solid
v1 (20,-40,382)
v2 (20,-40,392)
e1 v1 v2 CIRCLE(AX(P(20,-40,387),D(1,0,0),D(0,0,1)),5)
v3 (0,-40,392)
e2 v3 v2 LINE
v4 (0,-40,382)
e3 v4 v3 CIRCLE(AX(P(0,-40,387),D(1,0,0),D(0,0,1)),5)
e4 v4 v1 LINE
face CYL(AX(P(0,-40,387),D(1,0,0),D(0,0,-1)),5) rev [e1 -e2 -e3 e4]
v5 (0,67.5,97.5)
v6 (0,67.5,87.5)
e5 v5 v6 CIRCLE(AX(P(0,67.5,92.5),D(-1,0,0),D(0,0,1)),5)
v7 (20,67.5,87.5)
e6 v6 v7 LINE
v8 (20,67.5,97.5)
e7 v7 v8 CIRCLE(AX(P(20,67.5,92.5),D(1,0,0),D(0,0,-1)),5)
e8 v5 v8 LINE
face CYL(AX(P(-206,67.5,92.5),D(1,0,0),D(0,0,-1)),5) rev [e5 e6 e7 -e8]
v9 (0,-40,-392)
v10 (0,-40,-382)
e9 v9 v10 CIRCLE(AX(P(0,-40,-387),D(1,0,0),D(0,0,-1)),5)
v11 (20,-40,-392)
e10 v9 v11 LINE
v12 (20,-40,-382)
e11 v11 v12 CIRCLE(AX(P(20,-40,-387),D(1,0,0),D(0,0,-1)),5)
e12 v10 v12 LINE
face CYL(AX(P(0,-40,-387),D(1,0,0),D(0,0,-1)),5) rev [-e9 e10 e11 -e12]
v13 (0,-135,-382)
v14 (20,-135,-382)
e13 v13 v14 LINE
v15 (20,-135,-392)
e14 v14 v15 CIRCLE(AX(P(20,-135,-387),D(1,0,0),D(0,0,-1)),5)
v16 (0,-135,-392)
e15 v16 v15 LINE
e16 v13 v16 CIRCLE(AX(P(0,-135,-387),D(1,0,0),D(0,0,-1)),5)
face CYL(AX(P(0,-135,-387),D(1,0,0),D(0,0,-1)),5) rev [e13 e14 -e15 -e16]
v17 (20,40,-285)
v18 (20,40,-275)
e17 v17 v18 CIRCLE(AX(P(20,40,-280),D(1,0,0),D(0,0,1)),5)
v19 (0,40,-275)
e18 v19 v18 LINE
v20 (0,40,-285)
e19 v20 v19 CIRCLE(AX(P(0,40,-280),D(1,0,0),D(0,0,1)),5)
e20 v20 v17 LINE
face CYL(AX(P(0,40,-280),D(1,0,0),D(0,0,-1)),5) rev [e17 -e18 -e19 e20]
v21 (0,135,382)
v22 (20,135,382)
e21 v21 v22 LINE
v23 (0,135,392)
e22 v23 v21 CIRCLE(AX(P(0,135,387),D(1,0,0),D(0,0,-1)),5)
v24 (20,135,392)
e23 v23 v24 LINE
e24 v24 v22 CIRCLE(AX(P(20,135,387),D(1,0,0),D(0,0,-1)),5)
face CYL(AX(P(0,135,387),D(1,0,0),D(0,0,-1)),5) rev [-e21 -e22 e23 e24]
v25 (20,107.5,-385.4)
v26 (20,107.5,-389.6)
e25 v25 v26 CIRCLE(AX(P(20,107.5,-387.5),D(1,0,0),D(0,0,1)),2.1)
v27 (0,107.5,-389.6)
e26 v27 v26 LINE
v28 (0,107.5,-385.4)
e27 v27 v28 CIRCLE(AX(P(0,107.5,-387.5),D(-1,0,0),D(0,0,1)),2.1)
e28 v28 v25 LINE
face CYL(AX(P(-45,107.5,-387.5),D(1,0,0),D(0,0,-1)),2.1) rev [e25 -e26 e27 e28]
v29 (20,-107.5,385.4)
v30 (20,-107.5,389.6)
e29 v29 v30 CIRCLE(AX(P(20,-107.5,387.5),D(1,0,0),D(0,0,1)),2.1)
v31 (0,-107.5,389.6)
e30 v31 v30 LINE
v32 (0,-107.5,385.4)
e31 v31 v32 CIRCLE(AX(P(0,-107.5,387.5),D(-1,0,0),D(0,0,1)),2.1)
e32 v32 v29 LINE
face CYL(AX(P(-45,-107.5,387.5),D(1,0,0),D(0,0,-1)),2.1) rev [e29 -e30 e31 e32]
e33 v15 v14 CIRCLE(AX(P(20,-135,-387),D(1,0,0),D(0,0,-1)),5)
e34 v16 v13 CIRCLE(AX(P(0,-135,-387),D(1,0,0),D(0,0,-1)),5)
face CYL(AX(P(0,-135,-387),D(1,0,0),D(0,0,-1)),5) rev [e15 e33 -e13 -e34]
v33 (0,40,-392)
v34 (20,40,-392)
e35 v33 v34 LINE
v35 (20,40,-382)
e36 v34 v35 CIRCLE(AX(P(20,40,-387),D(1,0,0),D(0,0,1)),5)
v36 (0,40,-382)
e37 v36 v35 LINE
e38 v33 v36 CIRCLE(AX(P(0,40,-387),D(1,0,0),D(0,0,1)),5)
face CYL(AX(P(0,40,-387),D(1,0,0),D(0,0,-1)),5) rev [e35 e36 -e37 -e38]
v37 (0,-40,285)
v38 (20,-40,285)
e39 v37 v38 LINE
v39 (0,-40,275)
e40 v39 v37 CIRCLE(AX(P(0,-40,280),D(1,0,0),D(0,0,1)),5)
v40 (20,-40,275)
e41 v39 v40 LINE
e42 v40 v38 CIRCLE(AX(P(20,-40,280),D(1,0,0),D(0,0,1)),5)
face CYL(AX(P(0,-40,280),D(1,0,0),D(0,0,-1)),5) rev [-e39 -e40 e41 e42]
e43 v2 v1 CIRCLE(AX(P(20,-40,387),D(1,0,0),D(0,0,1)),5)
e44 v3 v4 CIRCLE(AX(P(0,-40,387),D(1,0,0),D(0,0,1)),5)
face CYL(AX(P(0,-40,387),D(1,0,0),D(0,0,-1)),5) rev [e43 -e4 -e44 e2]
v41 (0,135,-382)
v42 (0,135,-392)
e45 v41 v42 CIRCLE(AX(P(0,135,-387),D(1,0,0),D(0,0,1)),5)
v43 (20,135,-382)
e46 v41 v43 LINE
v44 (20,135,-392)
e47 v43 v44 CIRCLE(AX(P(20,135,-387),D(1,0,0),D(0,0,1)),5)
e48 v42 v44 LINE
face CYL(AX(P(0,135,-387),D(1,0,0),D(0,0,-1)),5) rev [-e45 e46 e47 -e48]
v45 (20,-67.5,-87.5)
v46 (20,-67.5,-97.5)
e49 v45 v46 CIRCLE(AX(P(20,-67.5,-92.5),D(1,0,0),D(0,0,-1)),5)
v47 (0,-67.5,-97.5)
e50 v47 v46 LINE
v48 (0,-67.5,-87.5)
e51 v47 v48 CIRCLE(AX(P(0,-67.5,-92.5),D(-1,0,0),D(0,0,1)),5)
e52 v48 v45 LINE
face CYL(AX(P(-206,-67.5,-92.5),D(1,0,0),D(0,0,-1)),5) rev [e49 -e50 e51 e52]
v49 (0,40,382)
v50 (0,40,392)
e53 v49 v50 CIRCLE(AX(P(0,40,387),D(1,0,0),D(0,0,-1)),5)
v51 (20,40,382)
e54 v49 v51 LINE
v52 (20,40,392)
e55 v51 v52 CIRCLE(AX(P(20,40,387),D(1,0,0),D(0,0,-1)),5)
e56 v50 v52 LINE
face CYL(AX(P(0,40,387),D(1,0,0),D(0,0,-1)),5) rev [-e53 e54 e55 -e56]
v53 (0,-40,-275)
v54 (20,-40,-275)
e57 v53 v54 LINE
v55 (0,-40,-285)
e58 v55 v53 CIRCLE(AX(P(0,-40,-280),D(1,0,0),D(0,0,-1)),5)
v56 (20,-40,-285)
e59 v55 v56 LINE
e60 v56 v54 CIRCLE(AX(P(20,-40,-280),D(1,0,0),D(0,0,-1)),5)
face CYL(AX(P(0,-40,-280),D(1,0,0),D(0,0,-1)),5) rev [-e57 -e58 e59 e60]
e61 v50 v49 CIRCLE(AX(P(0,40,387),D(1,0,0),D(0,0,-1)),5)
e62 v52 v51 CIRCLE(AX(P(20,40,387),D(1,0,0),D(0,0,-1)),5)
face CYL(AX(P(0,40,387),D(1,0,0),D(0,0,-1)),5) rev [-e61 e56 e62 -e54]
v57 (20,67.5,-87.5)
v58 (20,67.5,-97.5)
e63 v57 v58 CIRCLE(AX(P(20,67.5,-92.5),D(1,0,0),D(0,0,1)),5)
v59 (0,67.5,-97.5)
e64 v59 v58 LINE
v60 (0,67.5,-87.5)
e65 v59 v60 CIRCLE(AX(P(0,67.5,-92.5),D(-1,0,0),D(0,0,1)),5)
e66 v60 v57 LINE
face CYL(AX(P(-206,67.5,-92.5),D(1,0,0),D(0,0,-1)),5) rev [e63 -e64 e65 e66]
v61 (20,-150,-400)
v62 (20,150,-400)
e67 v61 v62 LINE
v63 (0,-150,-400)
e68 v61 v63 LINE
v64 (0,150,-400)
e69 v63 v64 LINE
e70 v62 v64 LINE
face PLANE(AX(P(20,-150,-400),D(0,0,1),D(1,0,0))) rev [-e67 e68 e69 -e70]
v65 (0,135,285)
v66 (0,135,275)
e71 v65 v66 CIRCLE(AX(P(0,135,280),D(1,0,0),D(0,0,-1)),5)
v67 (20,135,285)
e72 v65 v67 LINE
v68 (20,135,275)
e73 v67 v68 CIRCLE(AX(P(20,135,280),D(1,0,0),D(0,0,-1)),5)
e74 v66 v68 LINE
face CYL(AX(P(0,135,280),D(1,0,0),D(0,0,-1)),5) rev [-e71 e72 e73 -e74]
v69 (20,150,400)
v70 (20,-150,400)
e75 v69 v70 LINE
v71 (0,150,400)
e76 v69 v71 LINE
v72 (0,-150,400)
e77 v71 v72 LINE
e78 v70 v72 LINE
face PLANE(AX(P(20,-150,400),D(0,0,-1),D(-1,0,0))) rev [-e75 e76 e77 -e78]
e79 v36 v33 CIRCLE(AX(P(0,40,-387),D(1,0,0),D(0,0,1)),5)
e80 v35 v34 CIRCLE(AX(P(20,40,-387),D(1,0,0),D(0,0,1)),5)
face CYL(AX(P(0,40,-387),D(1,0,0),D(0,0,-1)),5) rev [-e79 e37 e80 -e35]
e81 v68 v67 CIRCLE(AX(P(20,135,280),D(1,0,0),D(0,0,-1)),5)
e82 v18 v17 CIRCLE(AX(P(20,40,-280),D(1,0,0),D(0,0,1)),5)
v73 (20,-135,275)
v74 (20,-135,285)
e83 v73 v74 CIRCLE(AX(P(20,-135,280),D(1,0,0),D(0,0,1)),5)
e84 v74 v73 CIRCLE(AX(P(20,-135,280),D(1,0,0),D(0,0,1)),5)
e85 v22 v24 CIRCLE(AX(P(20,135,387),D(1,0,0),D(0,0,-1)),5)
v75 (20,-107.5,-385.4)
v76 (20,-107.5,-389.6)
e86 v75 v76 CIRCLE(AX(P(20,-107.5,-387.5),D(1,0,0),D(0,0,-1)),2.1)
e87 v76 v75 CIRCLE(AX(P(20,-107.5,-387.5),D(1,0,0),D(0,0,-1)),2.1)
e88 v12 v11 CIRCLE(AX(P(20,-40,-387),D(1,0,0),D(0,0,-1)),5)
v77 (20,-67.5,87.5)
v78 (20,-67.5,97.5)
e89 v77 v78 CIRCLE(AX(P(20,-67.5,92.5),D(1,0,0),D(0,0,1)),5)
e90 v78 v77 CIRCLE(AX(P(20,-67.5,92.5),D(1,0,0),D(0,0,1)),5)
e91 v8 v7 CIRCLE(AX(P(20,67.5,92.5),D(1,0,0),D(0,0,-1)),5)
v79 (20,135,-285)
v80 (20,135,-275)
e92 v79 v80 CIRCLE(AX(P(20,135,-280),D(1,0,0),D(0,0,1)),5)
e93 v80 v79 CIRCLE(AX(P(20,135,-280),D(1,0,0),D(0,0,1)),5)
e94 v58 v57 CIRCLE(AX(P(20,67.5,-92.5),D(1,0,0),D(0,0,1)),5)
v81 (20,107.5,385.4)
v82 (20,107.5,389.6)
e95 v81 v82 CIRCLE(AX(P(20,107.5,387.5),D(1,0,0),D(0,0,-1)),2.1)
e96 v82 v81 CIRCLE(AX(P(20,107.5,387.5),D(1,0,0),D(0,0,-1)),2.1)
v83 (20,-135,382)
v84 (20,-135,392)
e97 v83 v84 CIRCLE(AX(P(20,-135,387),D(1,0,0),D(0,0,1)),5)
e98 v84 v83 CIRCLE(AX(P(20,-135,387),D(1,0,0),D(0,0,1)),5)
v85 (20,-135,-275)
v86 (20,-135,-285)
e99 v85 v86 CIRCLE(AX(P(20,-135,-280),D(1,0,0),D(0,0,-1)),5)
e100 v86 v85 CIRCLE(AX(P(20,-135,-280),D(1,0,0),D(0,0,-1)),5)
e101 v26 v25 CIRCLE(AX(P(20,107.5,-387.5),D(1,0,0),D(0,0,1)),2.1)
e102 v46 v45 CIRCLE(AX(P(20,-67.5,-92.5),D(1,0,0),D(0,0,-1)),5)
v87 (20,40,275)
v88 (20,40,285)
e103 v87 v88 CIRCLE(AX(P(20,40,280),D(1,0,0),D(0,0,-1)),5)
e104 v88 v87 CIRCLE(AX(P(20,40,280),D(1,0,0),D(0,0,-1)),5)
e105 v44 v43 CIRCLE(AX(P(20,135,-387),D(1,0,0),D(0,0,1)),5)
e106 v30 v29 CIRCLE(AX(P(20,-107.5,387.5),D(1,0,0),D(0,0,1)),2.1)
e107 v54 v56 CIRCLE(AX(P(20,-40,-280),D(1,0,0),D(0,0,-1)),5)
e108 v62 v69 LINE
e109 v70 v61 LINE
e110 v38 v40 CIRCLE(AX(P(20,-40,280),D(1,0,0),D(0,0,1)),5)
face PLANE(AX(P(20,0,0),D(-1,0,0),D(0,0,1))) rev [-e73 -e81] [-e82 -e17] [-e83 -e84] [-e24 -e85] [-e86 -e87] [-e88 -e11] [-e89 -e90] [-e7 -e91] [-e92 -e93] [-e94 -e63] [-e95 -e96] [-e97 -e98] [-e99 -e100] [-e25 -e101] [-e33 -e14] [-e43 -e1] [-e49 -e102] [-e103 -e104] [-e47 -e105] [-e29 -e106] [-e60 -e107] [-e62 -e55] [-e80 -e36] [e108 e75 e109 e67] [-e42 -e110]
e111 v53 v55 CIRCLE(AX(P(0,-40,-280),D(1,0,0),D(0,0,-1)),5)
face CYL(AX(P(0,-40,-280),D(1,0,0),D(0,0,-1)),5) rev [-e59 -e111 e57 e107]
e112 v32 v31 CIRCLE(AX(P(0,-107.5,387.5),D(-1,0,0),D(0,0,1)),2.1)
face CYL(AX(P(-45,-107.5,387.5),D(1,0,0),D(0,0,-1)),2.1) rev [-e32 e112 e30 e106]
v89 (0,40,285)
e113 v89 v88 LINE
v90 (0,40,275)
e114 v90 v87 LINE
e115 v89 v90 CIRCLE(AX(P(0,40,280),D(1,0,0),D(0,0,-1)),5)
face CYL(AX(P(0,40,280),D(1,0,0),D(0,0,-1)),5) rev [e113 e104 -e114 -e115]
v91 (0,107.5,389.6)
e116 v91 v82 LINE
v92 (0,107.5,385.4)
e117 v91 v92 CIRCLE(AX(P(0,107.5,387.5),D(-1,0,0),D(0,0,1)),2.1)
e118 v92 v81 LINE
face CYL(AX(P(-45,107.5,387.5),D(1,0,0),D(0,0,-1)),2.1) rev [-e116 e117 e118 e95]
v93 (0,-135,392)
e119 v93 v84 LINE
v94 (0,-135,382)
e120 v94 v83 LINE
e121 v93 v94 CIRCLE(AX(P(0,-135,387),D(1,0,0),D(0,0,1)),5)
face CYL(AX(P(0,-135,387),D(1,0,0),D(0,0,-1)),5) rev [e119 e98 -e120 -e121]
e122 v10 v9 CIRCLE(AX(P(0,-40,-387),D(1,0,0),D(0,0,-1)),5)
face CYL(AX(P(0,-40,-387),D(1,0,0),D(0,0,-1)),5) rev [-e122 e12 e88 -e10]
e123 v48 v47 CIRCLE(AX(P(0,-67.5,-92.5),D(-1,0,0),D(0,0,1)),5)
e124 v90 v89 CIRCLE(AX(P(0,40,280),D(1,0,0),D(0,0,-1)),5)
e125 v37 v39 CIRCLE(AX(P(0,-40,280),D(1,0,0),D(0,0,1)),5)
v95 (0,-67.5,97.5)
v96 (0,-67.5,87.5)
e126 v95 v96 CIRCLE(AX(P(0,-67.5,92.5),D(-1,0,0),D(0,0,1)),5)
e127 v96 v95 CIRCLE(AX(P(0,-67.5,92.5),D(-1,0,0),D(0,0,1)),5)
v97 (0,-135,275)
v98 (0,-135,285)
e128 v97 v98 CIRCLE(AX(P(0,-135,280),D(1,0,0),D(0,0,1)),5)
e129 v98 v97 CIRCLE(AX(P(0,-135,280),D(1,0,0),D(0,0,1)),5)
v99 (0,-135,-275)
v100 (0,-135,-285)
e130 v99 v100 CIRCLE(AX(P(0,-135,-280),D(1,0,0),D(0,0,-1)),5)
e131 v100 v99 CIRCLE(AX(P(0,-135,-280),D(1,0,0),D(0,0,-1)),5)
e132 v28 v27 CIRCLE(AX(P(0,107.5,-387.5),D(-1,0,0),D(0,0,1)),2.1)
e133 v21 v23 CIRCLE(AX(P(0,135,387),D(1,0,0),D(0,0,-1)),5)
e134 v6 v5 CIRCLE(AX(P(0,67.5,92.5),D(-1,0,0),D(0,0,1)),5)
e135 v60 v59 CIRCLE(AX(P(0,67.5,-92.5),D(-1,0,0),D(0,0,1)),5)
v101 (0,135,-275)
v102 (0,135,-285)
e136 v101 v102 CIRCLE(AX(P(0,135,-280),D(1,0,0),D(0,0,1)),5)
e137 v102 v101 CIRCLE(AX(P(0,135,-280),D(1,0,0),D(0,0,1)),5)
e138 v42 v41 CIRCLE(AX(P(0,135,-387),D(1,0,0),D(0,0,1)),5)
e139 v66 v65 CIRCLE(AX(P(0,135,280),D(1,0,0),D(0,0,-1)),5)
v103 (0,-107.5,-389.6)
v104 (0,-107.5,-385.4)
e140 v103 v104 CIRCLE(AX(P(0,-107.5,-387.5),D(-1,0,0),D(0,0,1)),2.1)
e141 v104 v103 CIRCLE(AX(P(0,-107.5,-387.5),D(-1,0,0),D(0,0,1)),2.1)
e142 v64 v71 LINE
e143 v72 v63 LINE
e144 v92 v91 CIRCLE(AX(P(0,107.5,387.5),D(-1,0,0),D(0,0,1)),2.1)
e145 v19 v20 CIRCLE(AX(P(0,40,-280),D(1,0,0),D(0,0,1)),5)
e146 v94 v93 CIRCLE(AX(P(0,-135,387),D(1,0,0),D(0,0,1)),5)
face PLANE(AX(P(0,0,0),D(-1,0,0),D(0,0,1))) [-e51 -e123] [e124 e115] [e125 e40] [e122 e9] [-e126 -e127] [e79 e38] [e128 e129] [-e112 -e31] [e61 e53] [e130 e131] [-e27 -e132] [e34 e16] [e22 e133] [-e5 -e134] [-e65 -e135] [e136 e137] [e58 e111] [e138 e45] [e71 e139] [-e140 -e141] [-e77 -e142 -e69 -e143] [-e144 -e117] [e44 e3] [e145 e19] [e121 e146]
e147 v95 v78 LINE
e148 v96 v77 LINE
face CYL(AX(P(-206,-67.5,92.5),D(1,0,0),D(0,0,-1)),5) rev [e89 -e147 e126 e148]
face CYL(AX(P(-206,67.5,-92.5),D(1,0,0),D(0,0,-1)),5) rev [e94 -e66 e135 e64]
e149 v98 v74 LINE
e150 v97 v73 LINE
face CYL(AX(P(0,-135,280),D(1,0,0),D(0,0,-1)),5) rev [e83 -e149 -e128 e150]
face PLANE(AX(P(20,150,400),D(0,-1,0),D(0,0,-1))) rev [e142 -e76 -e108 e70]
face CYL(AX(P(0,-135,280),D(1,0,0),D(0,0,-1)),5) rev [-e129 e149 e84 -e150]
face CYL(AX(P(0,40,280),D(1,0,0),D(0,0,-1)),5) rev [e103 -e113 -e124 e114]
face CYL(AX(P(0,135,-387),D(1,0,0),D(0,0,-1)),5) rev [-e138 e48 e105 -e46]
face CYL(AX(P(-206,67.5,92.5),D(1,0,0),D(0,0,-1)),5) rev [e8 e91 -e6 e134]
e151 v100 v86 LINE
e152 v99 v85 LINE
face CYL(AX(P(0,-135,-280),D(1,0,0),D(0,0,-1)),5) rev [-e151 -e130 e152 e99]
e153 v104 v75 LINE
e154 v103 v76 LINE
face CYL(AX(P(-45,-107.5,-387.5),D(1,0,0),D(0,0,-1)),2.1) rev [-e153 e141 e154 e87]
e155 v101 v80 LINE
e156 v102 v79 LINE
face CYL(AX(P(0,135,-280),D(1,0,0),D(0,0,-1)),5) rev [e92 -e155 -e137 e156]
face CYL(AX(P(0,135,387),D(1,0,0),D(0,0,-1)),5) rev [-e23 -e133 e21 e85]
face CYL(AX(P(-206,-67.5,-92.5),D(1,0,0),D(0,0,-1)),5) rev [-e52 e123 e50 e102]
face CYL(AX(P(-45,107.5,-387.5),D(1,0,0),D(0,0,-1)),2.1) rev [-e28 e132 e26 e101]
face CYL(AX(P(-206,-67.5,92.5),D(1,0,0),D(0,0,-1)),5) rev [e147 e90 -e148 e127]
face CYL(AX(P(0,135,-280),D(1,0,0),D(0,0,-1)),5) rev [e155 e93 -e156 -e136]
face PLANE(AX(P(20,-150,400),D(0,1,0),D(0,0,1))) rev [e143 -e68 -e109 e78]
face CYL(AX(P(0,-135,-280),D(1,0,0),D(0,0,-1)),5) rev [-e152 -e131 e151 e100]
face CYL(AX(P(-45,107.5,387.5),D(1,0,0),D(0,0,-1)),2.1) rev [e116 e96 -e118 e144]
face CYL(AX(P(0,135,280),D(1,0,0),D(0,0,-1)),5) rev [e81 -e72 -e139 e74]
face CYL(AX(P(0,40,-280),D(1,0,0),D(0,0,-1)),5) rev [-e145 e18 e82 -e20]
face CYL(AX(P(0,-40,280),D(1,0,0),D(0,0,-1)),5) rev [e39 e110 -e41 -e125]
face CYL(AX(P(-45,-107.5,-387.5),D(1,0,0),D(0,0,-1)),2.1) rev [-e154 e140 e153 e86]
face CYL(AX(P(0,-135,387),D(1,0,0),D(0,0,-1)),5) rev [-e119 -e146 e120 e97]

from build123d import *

# Parameters (mm, degrees)
SKETCH1_W           = 800
SKETCH1_H           = 300
BOSS_EXTRUDE1_DEPTH = 20
SKETCH2_R           = 5
CUT_EXTRUDE1_DEPTH  = 20
SKETCH3_R           = 2.1
CUT_EXTRUDE2_DEPTH  = 65
SKETCH4_R           = 5
CUT_EXTRUDE3_DEPTH  = 226


with BuildPart() as part:
    # Sketch1 → Boss-Extrude1 (new body)
    with BuildSketch(Plane(origin=(0, 0, 0), x_dir=(0, 0, -1), z_dir=(1, 0, 0))):
        Rectangle(SKETCH1_W, SKETCH1_H)
    extrude(amount=BOSS_EXTRUDE1_DEPTH)

    # Sketch2 → Cut-Extrude1 (cut)
    with BuildSketch(Plane(origin=(20, 0, 0), x_dir=(0, 0, -1), z_dir=(1, 0, 0))):
        with Locations((-387, 135)):
            Circle(SKETCH2_R)
        with Locations((-280, 135)):
            Circle(SKETCH2_R)
        with Locations((-280, 40)):
            Circle(SKETCH2_R)
        with Locations((-387, 40)):
            Circle(SKETCH2_R)
        with Locations(Location((-280, -40, 0), (0, 0, 180))):
            Circle(SKETCH2_R)
        with Locations(Location((-280, -135, 0), (0, 0, 180))):
            Circle(SKETCH2_R)
        with Locations(Location((-387, -135, 0), (0, 0, 180))):
            Circle(SKETCH2_R)
        with Locations(Location((-387, -40, 0), (0, 0, 180))):
            Circle(SKETCH2_R)
        with Locations((280, -40)):
            Circle(SKETCH2_R)
        with Locations((280, -135)):
            Circle(SKETCH2_R)
        with Locations((387, -135)):
            Circle(SKETCH2_R)
        with Locations((387, -40)):
            Circle(SKETCH2_R)
        with Locations(Location((280, 135, 0), (0, 0, 180))):
            Circle(SKETCH2_R)
        with Locations(Location((387, 135, 0), (0, 0, 180))):
            Circle(SKETCH2_R)
        with Locations(Location((387, 40, 0), (0, 0, 180))):
            Circle(SKETCH2_R)
        with Locations(Location((280, 40, 0), (0, 0, 180))):
            Circle(SKETCH2_R)
    extrude(amount=-CUT_EXTRUDE1_DEPTH, mode=Mode.SUBTRACT)

    # Sketch3 → Cut-Extrude2 (cut)
    with BuildSketch(Plane(origin=(20, 0, 0), x_dir=(0, 0, -1), z_dir=(1, 0, 0))):
        with Locations((387.5, -107.5)):
            Circle(SKETCH3_R)
        with Locations(Location((387.5, 107.5, 0), (0, 0, 180))):
            Circle(SKETCH3_R)
        with Locations(Location((-387.5, -107.5, 0), (0, 0, 180))):
            Circle(SKETCH3_R)
        with Locations((-387.5, 107.5)):
            Circle(SKETCH3_R)
    extrude(amount=-CUT_EXTRUDE2_DEPTH, mode=Mode.SUBTRACT)

    # Sketch4 → Cut-Extrude3 (cut)
    with BuildSketch(Plane(origin=(20, 0, 0), x_dir=(0, 0, -1), z_dir=(1, 0, 0))):
        with Locations((-92.5, 67.5)):
            Circle(SKETCH4_R)
        with Locations((92.5, 67.5)):
            Circle(SKETCH4_R)
        with Locations((92.5, -67.5)):
            Circle(SKETCH4_R)
        with Locations((-92.5, -67.5)):
            Circle(SKETCH4_R)
    extrude(amount=-CUT_EXTRUDE3_DEPTH, mode=Mode.SUBTRACT)


solid = part.part
